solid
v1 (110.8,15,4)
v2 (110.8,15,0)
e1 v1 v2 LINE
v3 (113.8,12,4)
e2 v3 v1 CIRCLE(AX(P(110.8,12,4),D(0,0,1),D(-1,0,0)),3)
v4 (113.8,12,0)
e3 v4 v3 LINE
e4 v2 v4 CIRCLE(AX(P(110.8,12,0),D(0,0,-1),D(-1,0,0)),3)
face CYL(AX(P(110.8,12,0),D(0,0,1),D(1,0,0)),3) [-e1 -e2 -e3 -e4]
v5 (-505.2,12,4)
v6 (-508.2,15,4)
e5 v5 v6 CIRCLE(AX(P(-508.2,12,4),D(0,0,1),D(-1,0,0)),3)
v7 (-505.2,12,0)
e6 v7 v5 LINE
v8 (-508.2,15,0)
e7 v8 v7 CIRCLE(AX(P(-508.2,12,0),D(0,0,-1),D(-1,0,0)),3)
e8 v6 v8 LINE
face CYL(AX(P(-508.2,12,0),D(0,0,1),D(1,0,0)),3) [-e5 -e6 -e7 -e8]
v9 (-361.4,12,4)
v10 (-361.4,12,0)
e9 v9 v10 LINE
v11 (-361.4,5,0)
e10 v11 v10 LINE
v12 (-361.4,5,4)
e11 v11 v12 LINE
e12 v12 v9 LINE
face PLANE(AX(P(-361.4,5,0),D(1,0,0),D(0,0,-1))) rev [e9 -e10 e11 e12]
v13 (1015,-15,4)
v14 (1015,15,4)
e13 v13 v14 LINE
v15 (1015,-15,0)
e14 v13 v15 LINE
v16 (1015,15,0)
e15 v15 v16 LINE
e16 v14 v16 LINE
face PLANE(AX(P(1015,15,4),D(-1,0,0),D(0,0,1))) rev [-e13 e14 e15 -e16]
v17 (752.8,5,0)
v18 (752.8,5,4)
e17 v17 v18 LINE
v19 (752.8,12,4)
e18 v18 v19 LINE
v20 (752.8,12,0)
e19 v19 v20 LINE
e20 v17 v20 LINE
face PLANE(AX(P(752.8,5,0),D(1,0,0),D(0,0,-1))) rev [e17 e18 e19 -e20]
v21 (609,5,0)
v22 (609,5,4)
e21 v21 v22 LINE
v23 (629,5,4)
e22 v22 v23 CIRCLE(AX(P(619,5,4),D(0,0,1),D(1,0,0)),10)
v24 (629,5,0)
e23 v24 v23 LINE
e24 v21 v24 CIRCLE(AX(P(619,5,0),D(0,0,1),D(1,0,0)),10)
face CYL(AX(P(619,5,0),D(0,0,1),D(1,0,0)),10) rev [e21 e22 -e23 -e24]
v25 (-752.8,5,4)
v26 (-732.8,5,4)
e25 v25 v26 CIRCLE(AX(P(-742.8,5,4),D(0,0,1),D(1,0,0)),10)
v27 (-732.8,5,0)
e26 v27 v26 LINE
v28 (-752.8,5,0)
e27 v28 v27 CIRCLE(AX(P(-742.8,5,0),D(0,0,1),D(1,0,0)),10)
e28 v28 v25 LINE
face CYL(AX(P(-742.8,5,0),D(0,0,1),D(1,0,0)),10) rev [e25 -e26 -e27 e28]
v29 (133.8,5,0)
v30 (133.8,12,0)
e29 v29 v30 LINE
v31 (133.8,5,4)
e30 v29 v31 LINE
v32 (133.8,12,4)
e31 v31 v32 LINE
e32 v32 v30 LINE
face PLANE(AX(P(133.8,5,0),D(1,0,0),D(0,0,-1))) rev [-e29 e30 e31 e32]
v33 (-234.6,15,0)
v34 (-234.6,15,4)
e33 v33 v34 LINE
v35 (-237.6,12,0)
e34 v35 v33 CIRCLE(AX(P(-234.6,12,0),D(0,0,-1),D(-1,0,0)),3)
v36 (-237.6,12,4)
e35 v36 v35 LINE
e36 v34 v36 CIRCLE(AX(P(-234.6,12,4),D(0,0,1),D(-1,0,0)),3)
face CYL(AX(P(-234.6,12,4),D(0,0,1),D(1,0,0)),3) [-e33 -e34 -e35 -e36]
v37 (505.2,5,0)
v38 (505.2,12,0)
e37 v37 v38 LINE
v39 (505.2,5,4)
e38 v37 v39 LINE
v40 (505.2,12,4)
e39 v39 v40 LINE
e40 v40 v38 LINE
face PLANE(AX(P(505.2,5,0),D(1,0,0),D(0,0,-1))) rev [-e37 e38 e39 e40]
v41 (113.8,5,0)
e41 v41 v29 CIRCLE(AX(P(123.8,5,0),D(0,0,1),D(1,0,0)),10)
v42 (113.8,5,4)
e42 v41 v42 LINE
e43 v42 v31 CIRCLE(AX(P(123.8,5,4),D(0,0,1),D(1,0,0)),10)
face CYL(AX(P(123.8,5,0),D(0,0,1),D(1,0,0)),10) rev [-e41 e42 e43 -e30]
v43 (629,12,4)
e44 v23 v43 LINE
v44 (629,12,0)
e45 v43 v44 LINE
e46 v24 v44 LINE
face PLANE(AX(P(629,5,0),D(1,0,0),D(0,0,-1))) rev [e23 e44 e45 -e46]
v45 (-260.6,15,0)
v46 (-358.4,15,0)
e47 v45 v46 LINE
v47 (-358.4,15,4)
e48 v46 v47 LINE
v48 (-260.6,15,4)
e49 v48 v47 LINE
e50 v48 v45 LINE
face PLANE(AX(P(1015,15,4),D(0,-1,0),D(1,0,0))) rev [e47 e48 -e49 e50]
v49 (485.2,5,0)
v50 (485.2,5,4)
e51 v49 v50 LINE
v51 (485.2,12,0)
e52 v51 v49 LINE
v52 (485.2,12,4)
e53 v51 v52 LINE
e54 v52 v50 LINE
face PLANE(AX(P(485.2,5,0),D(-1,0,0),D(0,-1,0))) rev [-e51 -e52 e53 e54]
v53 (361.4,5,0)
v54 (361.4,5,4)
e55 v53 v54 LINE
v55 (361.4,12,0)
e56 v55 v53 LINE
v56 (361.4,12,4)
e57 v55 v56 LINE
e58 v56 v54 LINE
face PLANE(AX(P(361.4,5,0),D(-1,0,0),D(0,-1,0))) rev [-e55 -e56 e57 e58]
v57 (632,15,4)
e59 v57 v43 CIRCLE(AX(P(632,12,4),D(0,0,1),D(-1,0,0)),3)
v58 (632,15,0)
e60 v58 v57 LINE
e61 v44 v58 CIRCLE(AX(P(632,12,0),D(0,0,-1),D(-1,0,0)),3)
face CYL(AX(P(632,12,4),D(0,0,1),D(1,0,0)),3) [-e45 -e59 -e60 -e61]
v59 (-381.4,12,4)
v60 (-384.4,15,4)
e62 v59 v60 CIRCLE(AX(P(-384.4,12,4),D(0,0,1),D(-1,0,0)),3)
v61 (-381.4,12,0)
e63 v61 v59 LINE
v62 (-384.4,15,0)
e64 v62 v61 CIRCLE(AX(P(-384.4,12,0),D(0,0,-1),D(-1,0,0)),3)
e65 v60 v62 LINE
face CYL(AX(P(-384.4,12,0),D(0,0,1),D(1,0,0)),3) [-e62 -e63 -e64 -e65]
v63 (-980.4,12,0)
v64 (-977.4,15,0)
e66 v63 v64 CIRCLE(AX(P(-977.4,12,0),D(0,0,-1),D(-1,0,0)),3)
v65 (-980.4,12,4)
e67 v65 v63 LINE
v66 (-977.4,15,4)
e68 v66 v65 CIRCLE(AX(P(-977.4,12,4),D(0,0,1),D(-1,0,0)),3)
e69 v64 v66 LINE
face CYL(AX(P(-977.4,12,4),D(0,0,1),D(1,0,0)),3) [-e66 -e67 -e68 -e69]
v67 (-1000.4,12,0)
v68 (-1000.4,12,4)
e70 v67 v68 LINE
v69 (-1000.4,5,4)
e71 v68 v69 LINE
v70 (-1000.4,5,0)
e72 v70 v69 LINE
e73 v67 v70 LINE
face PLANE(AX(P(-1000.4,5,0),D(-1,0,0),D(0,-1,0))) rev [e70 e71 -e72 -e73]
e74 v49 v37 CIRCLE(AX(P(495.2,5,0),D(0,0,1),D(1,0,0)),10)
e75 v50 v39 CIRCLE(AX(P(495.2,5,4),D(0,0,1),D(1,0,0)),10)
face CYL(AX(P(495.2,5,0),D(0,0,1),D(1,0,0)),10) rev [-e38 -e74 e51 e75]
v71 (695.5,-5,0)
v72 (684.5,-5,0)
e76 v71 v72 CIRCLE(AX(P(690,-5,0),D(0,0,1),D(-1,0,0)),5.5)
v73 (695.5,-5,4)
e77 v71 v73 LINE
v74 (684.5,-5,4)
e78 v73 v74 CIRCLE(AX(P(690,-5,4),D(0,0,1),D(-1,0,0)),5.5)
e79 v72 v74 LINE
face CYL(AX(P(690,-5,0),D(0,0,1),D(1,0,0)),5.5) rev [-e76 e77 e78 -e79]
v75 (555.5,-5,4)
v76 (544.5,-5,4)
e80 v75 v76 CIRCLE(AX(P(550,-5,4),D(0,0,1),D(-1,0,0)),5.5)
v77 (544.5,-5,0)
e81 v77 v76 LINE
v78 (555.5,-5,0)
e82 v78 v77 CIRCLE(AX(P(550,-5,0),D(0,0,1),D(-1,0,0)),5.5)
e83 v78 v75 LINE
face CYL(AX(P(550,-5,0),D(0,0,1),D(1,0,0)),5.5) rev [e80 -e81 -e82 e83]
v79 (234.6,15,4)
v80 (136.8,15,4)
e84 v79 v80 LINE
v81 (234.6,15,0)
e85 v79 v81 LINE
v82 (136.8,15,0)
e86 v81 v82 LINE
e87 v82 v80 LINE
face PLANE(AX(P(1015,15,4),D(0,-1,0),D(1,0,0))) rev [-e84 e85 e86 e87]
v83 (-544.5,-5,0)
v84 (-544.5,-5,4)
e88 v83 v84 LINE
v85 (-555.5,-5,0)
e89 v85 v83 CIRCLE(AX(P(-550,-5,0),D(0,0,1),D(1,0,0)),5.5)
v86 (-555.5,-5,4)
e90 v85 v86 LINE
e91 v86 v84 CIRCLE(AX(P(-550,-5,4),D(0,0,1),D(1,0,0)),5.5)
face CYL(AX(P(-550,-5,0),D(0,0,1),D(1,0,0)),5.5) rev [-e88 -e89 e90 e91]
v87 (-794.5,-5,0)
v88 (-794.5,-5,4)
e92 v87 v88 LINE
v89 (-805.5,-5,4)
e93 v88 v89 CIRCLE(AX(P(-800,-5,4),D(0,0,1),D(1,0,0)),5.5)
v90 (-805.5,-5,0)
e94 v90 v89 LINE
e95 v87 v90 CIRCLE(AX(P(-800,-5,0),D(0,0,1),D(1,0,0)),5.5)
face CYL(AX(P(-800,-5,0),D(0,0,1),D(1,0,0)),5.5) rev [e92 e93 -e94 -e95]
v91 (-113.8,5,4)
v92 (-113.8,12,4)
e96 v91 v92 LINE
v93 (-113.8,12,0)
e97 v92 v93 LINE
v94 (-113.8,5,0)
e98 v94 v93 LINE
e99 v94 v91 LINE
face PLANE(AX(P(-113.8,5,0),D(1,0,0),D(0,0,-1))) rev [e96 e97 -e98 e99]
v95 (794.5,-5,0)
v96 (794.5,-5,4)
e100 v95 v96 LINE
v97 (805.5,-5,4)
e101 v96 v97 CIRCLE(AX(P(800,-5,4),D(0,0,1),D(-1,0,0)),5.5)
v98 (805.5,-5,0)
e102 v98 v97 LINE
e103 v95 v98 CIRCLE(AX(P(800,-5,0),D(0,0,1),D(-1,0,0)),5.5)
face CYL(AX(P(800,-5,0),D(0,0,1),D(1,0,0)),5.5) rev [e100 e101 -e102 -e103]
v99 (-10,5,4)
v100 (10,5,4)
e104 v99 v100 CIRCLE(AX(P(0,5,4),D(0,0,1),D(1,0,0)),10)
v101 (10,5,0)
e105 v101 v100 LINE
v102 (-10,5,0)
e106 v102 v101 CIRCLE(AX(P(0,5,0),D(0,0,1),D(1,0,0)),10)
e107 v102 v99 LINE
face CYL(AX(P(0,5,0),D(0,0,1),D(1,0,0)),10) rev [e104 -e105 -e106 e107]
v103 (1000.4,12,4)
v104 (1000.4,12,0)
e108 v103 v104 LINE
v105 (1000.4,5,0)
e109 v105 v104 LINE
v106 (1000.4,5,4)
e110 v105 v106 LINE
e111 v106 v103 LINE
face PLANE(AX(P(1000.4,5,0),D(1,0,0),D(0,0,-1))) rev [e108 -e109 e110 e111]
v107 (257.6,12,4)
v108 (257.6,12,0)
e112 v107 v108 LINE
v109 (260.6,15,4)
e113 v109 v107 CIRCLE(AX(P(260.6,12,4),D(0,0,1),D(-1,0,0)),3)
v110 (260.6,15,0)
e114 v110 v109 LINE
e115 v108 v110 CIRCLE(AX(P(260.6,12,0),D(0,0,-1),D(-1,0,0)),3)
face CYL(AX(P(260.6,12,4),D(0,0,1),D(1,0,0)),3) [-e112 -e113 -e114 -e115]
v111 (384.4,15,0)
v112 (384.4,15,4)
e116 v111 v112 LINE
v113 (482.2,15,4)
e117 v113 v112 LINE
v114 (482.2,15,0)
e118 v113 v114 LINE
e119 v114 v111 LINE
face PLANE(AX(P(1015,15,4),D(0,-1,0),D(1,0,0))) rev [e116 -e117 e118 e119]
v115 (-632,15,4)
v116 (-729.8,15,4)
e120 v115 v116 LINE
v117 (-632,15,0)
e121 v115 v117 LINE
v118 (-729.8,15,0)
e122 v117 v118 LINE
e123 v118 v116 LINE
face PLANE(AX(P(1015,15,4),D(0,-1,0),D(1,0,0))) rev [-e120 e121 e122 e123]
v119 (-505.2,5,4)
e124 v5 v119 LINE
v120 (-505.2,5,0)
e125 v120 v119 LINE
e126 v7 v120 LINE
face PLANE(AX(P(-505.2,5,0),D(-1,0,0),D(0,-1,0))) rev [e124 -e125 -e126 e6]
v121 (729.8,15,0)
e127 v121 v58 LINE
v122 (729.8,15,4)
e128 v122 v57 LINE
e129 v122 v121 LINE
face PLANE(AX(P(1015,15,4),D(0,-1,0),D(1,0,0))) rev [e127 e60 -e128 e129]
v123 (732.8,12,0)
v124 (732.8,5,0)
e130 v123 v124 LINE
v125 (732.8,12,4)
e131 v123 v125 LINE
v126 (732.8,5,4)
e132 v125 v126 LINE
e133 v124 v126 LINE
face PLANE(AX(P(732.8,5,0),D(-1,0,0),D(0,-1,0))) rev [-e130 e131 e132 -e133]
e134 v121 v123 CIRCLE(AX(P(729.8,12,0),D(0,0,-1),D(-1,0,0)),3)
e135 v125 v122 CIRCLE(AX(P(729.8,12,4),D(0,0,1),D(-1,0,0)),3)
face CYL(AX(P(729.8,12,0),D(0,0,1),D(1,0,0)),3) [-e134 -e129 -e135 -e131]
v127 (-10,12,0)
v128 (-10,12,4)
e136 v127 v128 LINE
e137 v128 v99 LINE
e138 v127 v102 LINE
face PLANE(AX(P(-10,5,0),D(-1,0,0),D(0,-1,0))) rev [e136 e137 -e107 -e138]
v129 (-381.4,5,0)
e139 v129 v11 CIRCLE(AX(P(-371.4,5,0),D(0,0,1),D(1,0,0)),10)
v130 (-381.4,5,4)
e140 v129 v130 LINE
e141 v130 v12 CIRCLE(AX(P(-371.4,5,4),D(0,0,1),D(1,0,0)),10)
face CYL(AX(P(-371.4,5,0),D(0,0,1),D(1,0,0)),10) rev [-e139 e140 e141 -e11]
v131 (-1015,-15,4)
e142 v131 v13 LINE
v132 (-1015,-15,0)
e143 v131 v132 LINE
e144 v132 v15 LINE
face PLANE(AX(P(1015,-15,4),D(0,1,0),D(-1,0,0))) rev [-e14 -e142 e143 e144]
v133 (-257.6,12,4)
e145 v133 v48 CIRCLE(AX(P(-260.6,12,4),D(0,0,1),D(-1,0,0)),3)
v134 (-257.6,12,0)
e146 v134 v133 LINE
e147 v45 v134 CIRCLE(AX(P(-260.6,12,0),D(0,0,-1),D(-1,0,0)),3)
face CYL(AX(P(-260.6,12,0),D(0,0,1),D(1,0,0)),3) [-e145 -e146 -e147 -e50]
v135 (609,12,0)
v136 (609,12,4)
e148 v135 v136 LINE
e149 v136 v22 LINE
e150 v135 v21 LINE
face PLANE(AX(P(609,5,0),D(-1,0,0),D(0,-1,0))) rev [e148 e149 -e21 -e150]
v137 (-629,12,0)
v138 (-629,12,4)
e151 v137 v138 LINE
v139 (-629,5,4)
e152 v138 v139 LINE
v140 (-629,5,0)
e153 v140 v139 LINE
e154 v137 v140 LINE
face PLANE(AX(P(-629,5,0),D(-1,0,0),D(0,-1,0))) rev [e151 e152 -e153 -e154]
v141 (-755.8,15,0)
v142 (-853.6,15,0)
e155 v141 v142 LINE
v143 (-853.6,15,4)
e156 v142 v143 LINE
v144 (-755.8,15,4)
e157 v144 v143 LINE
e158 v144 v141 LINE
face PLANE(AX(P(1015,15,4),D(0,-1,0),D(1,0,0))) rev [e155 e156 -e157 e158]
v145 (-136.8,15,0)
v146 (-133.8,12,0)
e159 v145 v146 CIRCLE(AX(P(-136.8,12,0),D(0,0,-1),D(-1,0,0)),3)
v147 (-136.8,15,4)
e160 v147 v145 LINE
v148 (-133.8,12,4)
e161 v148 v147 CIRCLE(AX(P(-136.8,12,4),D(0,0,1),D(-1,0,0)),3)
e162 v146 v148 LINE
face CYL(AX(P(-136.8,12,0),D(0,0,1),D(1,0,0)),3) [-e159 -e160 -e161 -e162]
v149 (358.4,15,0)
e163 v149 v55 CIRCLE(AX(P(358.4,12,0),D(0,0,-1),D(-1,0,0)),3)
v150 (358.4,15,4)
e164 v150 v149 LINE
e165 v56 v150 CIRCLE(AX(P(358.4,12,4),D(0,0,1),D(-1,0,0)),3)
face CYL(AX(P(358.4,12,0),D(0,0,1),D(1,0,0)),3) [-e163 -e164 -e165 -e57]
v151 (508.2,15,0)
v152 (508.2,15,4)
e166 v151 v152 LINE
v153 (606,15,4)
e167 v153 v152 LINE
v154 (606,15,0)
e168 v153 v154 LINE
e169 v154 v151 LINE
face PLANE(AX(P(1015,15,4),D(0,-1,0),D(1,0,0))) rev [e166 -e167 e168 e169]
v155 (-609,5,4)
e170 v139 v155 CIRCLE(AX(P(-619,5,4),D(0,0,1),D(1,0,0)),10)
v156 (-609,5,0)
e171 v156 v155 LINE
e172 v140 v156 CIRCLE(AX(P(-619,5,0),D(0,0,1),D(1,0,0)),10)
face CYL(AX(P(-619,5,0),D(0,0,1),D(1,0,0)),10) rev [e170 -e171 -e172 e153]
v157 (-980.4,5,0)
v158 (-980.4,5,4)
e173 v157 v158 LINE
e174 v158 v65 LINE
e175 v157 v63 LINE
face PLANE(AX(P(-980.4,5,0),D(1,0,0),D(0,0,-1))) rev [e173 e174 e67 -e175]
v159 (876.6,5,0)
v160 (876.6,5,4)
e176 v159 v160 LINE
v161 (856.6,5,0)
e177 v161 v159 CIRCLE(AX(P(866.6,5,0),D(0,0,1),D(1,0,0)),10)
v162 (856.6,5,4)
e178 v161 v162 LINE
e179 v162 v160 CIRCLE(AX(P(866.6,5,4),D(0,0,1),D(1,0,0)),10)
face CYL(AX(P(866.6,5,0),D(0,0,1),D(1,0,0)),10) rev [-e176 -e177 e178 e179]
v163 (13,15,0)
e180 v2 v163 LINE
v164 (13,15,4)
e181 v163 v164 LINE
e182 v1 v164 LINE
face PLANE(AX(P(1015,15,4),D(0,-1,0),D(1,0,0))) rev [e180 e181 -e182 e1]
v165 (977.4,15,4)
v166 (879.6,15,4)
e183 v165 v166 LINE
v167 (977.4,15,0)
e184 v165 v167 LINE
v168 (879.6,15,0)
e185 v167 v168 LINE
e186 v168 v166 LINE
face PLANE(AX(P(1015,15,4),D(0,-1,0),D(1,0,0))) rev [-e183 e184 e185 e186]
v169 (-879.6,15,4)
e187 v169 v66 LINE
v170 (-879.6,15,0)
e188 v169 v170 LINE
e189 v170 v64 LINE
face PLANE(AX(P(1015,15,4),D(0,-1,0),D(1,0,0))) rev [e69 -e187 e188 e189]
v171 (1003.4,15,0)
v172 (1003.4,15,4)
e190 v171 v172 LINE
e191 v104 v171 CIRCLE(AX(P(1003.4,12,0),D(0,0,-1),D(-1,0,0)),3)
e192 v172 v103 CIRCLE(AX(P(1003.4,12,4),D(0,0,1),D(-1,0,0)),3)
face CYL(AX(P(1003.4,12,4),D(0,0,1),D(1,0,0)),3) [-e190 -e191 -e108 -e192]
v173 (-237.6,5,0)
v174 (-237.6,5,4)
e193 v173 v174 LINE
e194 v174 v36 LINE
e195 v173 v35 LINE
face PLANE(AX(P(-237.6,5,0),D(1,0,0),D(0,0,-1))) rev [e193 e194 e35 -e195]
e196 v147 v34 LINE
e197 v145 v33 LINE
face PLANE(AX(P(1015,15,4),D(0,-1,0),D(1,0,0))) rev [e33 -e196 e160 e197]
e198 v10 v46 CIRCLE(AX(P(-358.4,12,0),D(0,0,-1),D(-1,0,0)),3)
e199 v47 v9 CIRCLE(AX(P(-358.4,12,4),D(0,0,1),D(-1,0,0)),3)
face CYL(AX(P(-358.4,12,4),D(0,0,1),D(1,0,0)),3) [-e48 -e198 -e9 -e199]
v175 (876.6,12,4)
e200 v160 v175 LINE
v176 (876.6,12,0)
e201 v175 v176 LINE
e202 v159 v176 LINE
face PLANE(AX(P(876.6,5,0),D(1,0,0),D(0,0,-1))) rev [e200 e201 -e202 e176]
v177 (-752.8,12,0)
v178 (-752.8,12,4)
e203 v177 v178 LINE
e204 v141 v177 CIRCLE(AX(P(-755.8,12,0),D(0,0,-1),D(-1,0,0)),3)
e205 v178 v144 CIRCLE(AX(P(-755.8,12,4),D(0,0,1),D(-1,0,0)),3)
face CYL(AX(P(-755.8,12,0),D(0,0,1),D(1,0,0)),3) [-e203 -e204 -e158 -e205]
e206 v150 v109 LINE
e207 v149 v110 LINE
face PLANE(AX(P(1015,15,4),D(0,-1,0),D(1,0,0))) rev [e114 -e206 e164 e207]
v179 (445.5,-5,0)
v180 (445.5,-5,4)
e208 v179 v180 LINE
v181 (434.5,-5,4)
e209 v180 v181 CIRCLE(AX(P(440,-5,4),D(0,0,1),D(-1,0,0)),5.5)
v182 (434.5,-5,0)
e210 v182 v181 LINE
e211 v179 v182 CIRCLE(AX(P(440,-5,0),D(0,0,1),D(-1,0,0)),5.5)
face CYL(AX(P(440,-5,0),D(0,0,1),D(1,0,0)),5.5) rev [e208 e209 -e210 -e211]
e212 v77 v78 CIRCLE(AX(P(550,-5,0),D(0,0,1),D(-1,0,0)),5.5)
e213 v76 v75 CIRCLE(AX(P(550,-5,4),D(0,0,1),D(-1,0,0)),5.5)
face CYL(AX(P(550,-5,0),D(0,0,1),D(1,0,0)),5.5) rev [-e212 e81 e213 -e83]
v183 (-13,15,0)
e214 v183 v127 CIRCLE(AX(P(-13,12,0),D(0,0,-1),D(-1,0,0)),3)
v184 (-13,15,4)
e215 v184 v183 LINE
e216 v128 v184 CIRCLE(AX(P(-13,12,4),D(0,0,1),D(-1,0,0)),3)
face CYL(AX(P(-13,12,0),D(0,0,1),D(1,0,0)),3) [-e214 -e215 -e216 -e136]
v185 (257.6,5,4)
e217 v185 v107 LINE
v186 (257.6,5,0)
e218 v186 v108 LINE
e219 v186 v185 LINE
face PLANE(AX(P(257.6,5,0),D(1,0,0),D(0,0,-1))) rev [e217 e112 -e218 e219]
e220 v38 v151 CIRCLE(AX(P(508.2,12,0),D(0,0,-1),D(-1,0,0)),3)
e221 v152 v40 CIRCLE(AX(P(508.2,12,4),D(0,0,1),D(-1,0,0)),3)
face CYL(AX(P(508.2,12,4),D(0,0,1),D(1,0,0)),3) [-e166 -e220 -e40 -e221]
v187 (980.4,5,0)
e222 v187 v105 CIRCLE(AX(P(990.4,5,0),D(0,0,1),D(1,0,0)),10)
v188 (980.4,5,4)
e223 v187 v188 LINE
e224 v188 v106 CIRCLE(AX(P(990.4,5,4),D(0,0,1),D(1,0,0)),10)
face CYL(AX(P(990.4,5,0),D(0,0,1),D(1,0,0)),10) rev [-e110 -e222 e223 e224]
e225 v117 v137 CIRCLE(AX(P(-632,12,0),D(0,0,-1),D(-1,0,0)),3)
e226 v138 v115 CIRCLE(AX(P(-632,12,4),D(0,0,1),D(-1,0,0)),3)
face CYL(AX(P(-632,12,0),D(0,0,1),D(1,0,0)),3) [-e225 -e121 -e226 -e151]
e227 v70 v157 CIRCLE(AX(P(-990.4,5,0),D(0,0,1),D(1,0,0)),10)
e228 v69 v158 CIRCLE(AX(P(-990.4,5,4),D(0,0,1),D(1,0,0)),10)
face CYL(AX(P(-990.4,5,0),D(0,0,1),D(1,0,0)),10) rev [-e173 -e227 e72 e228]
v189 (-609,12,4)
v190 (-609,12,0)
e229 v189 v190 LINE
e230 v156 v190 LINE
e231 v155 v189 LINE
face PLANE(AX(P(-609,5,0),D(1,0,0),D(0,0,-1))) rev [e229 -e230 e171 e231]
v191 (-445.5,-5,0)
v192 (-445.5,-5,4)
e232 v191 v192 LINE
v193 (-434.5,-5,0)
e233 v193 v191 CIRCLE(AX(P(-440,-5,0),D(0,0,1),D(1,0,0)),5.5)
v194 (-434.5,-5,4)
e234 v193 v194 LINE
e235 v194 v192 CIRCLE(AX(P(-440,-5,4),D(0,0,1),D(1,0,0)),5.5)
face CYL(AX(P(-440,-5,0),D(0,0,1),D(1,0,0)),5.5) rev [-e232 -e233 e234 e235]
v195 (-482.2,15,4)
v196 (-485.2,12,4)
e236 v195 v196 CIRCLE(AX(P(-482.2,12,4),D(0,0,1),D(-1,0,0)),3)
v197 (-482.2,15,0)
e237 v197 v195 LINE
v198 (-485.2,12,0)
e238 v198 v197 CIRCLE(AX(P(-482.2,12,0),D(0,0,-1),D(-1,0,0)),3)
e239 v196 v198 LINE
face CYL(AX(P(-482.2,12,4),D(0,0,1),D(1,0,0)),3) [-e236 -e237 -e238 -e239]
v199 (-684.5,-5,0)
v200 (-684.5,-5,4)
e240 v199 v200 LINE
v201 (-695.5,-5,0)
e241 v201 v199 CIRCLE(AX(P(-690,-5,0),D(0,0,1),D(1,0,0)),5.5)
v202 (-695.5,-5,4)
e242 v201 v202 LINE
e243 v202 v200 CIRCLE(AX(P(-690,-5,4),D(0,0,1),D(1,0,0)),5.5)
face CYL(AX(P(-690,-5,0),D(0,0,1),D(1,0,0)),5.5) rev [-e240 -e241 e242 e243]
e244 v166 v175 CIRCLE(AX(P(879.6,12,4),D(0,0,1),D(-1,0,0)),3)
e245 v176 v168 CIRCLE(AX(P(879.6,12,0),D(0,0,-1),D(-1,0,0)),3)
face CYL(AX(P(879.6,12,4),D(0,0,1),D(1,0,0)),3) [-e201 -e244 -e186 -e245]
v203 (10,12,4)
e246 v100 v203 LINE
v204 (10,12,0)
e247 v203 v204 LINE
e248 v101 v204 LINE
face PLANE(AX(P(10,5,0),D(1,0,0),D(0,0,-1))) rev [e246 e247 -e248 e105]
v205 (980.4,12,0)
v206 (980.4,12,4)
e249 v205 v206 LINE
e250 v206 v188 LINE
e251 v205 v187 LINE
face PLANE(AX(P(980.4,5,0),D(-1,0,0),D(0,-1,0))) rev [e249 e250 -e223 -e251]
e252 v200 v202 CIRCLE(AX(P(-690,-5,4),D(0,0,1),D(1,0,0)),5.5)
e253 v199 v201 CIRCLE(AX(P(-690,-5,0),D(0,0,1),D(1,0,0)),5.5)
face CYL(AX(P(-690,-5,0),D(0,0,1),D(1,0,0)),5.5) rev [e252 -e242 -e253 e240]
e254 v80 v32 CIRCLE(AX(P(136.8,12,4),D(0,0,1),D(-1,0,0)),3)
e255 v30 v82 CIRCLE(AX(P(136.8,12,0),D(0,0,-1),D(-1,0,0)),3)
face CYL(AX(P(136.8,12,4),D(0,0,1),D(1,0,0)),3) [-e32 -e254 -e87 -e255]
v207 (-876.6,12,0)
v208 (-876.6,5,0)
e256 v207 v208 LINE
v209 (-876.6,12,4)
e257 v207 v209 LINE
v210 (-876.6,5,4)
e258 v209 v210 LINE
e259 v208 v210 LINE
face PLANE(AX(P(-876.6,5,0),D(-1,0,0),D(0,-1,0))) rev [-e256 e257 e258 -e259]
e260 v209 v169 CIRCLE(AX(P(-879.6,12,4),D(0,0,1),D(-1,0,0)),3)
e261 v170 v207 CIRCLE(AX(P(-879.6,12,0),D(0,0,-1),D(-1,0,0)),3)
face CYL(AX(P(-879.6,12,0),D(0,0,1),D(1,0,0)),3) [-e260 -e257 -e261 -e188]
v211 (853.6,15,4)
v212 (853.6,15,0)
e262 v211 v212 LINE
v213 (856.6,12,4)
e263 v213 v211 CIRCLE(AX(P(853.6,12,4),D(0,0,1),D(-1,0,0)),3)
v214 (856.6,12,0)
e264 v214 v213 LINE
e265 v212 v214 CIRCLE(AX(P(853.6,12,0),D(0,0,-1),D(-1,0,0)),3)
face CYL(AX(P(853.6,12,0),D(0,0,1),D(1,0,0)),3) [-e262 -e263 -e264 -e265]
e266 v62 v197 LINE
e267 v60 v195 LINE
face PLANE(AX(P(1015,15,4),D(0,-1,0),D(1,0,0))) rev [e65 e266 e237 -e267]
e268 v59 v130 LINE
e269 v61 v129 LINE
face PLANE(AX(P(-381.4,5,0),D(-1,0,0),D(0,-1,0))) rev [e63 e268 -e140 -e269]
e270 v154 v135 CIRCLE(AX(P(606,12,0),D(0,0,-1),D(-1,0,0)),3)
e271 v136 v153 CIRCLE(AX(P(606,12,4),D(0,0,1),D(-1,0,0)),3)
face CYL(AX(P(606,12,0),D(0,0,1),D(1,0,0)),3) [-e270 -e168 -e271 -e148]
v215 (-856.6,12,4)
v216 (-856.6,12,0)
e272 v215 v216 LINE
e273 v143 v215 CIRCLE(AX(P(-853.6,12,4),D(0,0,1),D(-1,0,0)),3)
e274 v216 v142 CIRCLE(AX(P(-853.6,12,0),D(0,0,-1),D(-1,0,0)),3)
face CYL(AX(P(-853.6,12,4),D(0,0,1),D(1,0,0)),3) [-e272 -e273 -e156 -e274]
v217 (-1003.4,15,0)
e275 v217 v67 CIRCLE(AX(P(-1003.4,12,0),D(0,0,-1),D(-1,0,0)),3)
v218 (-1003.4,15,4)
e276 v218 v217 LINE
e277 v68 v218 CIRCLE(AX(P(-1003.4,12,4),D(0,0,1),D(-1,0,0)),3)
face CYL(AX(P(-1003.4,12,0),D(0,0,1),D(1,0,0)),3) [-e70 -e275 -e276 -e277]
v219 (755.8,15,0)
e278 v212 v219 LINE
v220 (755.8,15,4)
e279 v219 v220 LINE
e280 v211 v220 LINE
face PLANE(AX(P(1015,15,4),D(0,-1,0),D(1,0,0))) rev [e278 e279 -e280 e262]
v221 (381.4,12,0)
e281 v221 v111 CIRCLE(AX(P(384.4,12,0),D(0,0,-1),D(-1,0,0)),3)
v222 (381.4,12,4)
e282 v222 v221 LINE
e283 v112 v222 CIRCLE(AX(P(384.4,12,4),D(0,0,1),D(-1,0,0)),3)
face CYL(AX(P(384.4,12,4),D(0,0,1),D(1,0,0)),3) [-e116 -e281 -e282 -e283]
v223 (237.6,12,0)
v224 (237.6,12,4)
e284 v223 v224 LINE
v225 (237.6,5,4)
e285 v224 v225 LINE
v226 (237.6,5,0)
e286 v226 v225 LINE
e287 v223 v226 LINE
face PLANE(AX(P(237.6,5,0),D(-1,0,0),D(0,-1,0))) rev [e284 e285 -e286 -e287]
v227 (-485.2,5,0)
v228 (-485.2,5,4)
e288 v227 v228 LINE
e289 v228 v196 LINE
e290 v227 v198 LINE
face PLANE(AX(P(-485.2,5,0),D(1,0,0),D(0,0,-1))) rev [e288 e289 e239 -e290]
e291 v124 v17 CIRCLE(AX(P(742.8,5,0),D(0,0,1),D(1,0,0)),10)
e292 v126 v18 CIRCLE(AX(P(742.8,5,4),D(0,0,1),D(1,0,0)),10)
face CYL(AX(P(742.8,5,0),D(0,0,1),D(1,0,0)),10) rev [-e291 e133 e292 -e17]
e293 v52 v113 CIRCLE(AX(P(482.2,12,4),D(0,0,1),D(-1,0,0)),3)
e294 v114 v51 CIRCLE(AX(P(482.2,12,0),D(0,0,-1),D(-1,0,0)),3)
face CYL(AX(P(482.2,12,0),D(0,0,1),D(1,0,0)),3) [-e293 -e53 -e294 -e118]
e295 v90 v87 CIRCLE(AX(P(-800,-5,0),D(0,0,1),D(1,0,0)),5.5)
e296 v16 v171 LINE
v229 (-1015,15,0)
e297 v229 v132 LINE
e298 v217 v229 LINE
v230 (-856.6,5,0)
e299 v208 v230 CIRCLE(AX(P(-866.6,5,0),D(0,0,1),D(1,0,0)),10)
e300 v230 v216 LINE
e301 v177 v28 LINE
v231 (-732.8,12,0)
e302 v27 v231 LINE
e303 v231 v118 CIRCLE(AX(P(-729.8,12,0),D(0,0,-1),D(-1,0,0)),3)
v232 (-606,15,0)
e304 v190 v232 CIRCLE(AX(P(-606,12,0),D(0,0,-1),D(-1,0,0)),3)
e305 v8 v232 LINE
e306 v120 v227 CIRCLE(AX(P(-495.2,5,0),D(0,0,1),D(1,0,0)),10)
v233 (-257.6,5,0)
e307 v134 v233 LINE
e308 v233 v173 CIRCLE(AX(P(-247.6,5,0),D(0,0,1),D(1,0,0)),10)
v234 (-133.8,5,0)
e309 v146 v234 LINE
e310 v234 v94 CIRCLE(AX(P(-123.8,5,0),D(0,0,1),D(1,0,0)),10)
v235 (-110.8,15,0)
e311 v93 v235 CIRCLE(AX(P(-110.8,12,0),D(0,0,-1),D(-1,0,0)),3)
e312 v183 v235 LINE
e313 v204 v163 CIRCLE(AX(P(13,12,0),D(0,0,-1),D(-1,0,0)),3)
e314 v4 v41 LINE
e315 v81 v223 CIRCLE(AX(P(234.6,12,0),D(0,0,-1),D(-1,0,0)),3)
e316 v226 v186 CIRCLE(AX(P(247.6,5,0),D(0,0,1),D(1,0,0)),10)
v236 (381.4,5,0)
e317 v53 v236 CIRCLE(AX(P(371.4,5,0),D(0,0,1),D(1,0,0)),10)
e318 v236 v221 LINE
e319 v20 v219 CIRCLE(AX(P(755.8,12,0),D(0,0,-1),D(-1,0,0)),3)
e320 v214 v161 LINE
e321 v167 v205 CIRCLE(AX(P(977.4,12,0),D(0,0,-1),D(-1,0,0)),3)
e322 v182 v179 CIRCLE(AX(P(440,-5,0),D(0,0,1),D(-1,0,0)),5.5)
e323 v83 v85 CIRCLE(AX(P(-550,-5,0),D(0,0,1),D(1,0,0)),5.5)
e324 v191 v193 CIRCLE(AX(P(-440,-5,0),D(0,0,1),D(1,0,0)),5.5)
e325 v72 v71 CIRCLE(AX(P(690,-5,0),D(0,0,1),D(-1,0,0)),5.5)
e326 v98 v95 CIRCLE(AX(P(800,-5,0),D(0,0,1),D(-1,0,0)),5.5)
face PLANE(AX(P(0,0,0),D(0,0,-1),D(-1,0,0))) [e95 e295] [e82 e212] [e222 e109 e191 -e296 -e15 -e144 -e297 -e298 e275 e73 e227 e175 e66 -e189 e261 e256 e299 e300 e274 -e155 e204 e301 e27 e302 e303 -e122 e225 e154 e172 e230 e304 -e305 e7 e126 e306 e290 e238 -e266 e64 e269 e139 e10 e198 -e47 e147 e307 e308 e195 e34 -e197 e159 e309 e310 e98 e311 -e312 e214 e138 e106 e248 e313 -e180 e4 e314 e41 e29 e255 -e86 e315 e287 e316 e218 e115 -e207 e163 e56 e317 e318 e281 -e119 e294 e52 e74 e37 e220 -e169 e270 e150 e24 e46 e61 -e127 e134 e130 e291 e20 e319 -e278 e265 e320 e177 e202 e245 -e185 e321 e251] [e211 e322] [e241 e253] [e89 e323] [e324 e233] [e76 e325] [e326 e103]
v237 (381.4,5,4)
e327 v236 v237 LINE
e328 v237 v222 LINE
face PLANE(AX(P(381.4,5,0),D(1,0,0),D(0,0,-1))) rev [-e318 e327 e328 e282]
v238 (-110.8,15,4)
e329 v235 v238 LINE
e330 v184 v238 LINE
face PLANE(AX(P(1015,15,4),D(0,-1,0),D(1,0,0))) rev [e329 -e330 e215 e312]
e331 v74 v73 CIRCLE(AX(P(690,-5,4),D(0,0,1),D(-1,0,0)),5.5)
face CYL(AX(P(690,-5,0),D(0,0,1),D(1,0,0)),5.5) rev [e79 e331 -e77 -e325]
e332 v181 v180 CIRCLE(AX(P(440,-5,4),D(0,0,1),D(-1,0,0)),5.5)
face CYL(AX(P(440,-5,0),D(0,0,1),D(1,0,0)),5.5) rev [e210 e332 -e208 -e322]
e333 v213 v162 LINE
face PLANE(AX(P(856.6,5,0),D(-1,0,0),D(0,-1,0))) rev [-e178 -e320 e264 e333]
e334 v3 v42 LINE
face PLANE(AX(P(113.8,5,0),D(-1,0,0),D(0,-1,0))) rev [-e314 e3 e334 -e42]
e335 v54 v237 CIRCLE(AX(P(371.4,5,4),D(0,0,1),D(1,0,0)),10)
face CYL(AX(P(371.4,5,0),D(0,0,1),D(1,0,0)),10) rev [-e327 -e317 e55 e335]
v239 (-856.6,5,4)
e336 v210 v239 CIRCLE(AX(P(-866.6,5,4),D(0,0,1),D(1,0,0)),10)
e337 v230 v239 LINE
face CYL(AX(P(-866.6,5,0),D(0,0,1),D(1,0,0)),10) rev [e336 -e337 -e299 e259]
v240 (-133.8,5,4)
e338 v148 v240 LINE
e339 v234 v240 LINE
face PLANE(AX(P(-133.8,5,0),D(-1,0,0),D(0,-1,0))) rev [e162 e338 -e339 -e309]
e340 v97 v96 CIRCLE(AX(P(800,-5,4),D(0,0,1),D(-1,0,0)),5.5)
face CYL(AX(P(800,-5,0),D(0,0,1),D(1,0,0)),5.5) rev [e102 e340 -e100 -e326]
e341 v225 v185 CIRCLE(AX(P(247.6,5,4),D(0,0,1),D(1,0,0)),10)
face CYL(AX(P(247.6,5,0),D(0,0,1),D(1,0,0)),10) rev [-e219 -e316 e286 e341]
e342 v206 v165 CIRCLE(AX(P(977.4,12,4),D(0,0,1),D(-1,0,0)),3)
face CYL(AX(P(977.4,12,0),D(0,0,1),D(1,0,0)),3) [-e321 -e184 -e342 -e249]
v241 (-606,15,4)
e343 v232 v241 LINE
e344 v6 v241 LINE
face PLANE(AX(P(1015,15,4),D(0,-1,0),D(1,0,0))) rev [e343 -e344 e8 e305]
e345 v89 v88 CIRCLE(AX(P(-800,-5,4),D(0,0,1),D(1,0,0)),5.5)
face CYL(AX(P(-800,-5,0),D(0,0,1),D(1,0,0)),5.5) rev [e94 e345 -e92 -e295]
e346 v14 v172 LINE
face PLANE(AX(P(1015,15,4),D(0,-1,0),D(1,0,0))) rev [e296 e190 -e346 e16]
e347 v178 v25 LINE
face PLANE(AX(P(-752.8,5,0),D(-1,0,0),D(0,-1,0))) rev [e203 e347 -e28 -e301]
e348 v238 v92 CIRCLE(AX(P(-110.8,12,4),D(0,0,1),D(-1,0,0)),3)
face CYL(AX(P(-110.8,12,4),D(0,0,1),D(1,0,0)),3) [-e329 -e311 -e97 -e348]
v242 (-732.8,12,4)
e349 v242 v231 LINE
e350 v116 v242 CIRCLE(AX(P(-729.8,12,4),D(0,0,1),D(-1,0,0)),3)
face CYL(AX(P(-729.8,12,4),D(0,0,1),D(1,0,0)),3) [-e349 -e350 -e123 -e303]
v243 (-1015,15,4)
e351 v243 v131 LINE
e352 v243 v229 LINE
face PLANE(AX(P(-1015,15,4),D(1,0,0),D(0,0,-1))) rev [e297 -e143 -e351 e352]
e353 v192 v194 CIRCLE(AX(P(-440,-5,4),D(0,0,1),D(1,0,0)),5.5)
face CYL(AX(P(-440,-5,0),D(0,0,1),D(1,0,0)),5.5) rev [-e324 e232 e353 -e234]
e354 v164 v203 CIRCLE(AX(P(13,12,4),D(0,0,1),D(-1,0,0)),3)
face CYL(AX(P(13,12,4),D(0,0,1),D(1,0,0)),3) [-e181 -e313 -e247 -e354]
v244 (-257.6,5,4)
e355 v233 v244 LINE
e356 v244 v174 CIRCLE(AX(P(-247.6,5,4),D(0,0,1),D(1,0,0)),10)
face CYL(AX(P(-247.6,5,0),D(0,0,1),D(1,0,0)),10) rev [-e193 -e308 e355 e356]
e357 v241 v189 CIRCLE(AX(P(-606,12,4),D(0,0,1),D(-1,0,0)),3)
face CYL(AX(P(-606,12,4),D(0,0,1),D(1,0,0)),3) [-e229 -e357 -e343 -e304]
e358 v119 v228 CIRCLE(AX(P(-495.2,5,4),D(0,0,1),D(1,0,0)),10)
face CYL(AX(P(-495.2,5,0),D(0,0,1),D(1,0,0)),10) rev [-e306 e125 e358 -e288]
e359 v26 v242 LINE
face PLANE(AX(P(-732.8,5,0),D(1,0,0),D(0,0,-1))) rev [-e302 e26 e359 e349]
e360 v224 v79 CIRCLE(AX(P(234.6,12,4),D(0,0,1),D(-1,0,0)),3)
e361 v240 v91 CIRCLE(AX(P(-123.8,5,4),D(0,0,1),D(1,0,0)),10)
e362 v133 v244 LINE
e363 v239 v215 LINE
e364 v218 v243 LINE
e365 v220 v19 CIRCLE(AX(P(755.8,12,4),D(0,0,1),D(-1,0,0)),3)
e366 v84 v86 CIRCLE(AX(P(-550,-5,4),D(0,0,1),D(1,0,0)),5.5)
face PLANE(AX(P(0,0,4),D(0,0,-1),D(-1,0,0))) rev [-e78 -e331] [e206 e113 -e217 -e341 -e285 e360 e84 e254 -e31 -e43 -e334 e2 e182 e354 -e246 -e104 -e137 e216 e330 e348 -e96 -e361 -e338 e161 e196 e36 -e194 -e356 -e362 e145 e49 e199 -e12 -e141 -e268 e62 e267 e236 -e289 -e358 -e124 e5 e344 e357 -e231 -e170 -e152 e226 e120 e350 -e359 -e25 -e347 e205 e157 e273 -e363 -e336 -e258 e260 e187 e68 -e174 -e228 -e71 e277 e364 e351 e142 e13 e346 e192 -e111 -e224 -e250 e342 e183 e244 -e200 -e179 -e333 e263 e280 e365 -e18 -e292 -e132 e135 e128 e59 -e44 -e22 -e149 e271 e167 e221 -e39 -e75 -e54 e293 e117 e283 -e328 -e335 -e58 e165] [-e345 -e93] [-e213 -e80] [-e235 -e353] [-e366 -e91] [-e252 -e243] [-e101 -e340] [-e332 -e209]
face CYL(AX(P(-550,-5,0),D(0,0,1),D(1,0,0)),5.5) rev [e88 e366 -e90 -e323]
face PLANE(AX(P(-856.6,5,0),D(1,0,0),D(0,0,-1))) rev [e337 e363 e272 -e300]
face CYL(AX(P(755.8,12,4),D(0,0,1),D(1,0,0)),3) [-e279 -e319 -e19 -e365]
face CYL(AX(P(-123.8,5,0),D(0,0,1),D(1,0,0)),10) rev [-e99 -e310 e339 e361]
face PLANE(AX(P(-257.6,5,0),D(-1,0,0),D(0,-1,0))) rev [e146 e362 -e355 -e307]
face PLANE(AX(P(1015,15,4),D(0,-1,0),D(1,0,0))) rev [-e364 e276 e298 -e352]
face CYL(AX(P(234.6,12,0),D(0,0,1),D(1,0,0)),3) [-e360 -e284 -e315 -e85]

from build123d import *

# Parameters (mm, degrees)
SKETCH_1_W          = 2030
SKETCH_1_H          = 30
EXTRUDE_1_DEPTH     = 4
CUT_EXTRUDE_1_DEPTH = 4
FILLET_1_R          = 3
SKETCH_3_R          = 5.5
CUT_EXTRUDE_2_DEPTH = 4


with BuildPart() as part:
    # 草图1 → 凸台-拉伸1 (new body)
    with BuildSketch(Plane.XY):
        Rectangle(SKETCH_1_W, SKETCH_1_H)
    extrude(amount=EXTRUDE_1_DEPTH)

    # 草图2 → 切除-拉伸1 (cut)
    with BuildSketch(Plane.XY.offset(4)):
        with BuildLine():
            Line((-1000.4, 5), (-1000.4, 15))
            Line((-1000.4, 15), (-980.4, 15))
            Line((-980.4, 15), (-980.4, 5))
            ThreePointArc((-980.4, 5), (-990.4, -5), (-1000.4, 5))
        make_face()
        with BuildLine():
            Line((-856.6, 15), (-876.6, 15))
            Line((-876.6, 15), (-876.6, 5))
            ThreePointArc((-876.6, 5), (-866.6, -5), (-856.6, 5))
            Line((-856.6, 5), (-856.6, 15))
        make_face()
        with BuildLine():
            Line((-732.8, 15), (-752.8, 15))
            Line((-752.8, 15), (-752.8, 5))
            ThreePointArc((-752.8, 5), (-742.8, -5), (-732.8, 5))
            Line((-732.8, 5), (-732.8, 15))
        make_face()
        with BuildLine():
            Line((-609, 15), (-629, 15))
            Line((-629, 15), (-629, 5))
            ThreePointArc((-629, 5), (-619, -5), (-609, 5))
            Line((-609, 5), (-609, 15))
        make_face()
        with BuildLine():
            Line((-485.2, 15), (-505.2, 15))
            Line((-505.2, 15), (-505.2, 5))
            ThreePointArc((-505.2, 5), (-495.2, -5), (-485.2, 5))
            Line((-485.2, 5), (-485.2, 15))
        make_face()
        with BuildLine():
            Line((-361.4, 15), (-381.4, 15))
            Line((-381.4, 15), (-381.4, 5))
            ThreePointArc((-381.4, 5), (-371.4, -5), (-361.4, 5))
            Line((-361.4, 5), (-361.4, 15))
        make_face()
        with BuildLine():
            Line((-237.6, 15), (-257.6, 15))
            Line((-257.6, 15), (-257.6, 5))
            ThreePointArc((-257.6, 5), (-247.6, -5), (-237.6, 5))
            Line((-237.6, 5), (-237.6, 15))
        make_face()
        with BuildLine():
            Line((-113.8, 15), (-133.8, 15))
            Line((-133.8, 15), (-133.8, 5))
            ThreePointArc((-133.8, 5), (-123.8, -5), (-113.8, 5))
            Line((-113.8, 5), (-113.8, 15))
        make_face()
        with BuildLine():
            Line((10, 15), (-10, 15))
            Line((-10, 15), (-10, 5))
            ThreePointArc((-10, 5), (0, -5), (10, 5))
            Line((10, 5), (10, 15))
        make_face()
        with BuildLine():
            Line((133.8, 15), (113.8, 15))
            Line((113.8, 15), (113.8, 5))
            ThreePointArc((113.8, 5), (123.8, -5), (133.8, 5))
            Line((133.8, 5), (133.8, 15))
        make_face()
        with BuildLine():
            Line((257.6, 15), (237.6, 15))
            Line((237.6, 15), (237.6, 5))
            ThreePointArc((237.6, 5), (247.6, -5), (257.6, 5))
            Line((257.6, 5), (257.6, 15))
        make_face()
        with BuildLine():
            Line((381.4, 15), (361.4, 15))
            Line((361.4, 15), (361.4, 5))
            ThreePointArc((361.4, 5), (371.4, -5), (381.4, 5))
            Line((381.4, 5), (381.4, 15))
        make_face()
        with BuildLine():
            Line((505.2, 15), (485.2, 15))
            Line((485.2, 15), (485.2, 5))
            ThreePointArc((485.2, 5), (495.2, -5), (505.2, 5))
            Line((505.2, 5), (505.2, 15))
        make_face()
        with BuildLine():
            Line((629, 15), (609, 15))
            Line((609, 15), (609, 5))
            ThreePointArc((609, 5), (619, -5), (629, 5))
            Line((629, 5), (629, 15))
        make_face()
        with BuildLine():
            Line((752.8, 15), (732.8, 15))
            Line((732.8, 15), (732.8, 5))
            ThreePointArc((732.8, 5), (742.8, -5), (752.8, 5))
            Line((752.8, 5), (752.8, 15))
        make_face()
        with BuildLine():
            Line((876.6, 15), (856.6, 15))
            Line((856.6, 15), (856.6, 5))
            ThreePointArc((856.6, 5), (866.6, -5), (876.6, 5))
            Line((876.6, 5), (876.6, 15))
        make_face()
        with BuildLine():
            Line((1000.4, 15), (980.4, 15))
            Line((980.4, 15), (980.4, 5))
            ThreePointArc((980.4, 5), (990.4, -5), (1000.4, 5))
            Line((1000.4, 5), (1000.4, 15))
        make_face()
    extrude(amount=-CUT_EXTRUDE_1_DEPTH, mode=Mode.SUBTRACT)

    # 圆角1
    fillet_1_edges = [part.edges().sort_by_distance(p)[0] for p in [
        (-876.6, 15, 2),
        (-856.6, 15, 2),
        (-752.8, 15, 2),
        (-732.8, 15, 2),
        (-629, 15, 2),
        (-609, 15, 2),
        (-505.2, 15, 2),
        (-485.2, 15, 2),
        (-381.4, 15, 2),
        (-361.4, 15, 2),
        (-257.6, 15, 2),
        (-237.6, 15, 2),
        (-133.8, 15, 2),
        (-113.8, 15, 2),
        (-10, 15, 2),
        (10, 15, 2),
        (113.8, 15, 2),
        (133.8, 15, 2),
        (237.6, 15, 2),
        (257.6, 15, 2),
        (361.4, 15, 2),
        (381.4, 15, 2),
        (485.2, 15, 2),
        (505.2, 15, 2),
        (609, 15, 2),
        (629, 15, 2),
        (732.8, 15, 2),
        (752.8, 15, 2),
        (856.6, 15, 2),
        (876.6, 15, 2),
        (980.4, 15, 2),
        (1000.4, 15, 2),
        (-1000.4, 15, 2),
        (-980.4, 15, 2),
    ]]
    fillet(fillet_1_edges, radius=FILLET_1_R)

    # 草图3 → 切除-拉伸2 (cut)
    with BuildSketch(Plane.XY.offset(4)):
        with Locations((-800, -5)):
            Circle(SKETCH_3_R)
        with Locations((-690, -5)):
            Circle(SKETCH_3_R)
        with Locations((-550, -5)):
            Circle(SKETCH_3_R)
        with Locations((-440, -5)):
            Circle(SKETCH_3_R)
        with Locations(Location((440, -5, 0), (0, 0, 180))):
            Circle(SKETCH_3_R)
        with Locations(Location((550, -5, 0), (0, 0, 180))):
            Circle(SKETCH_3_R)
        with Locations(Location((690, -5, 0), (0, 0, 180))):
            Circle(SKETCH_3_R)
        with Locations(Location((800, -5, 0), (0, 0, 180))):
            Circle(SKETCH_3_R)
    extrude(amount=-CUT_EXTRUDE_2_DEPTH, mode=Mode.SUBTRACT)


solid = part.part
